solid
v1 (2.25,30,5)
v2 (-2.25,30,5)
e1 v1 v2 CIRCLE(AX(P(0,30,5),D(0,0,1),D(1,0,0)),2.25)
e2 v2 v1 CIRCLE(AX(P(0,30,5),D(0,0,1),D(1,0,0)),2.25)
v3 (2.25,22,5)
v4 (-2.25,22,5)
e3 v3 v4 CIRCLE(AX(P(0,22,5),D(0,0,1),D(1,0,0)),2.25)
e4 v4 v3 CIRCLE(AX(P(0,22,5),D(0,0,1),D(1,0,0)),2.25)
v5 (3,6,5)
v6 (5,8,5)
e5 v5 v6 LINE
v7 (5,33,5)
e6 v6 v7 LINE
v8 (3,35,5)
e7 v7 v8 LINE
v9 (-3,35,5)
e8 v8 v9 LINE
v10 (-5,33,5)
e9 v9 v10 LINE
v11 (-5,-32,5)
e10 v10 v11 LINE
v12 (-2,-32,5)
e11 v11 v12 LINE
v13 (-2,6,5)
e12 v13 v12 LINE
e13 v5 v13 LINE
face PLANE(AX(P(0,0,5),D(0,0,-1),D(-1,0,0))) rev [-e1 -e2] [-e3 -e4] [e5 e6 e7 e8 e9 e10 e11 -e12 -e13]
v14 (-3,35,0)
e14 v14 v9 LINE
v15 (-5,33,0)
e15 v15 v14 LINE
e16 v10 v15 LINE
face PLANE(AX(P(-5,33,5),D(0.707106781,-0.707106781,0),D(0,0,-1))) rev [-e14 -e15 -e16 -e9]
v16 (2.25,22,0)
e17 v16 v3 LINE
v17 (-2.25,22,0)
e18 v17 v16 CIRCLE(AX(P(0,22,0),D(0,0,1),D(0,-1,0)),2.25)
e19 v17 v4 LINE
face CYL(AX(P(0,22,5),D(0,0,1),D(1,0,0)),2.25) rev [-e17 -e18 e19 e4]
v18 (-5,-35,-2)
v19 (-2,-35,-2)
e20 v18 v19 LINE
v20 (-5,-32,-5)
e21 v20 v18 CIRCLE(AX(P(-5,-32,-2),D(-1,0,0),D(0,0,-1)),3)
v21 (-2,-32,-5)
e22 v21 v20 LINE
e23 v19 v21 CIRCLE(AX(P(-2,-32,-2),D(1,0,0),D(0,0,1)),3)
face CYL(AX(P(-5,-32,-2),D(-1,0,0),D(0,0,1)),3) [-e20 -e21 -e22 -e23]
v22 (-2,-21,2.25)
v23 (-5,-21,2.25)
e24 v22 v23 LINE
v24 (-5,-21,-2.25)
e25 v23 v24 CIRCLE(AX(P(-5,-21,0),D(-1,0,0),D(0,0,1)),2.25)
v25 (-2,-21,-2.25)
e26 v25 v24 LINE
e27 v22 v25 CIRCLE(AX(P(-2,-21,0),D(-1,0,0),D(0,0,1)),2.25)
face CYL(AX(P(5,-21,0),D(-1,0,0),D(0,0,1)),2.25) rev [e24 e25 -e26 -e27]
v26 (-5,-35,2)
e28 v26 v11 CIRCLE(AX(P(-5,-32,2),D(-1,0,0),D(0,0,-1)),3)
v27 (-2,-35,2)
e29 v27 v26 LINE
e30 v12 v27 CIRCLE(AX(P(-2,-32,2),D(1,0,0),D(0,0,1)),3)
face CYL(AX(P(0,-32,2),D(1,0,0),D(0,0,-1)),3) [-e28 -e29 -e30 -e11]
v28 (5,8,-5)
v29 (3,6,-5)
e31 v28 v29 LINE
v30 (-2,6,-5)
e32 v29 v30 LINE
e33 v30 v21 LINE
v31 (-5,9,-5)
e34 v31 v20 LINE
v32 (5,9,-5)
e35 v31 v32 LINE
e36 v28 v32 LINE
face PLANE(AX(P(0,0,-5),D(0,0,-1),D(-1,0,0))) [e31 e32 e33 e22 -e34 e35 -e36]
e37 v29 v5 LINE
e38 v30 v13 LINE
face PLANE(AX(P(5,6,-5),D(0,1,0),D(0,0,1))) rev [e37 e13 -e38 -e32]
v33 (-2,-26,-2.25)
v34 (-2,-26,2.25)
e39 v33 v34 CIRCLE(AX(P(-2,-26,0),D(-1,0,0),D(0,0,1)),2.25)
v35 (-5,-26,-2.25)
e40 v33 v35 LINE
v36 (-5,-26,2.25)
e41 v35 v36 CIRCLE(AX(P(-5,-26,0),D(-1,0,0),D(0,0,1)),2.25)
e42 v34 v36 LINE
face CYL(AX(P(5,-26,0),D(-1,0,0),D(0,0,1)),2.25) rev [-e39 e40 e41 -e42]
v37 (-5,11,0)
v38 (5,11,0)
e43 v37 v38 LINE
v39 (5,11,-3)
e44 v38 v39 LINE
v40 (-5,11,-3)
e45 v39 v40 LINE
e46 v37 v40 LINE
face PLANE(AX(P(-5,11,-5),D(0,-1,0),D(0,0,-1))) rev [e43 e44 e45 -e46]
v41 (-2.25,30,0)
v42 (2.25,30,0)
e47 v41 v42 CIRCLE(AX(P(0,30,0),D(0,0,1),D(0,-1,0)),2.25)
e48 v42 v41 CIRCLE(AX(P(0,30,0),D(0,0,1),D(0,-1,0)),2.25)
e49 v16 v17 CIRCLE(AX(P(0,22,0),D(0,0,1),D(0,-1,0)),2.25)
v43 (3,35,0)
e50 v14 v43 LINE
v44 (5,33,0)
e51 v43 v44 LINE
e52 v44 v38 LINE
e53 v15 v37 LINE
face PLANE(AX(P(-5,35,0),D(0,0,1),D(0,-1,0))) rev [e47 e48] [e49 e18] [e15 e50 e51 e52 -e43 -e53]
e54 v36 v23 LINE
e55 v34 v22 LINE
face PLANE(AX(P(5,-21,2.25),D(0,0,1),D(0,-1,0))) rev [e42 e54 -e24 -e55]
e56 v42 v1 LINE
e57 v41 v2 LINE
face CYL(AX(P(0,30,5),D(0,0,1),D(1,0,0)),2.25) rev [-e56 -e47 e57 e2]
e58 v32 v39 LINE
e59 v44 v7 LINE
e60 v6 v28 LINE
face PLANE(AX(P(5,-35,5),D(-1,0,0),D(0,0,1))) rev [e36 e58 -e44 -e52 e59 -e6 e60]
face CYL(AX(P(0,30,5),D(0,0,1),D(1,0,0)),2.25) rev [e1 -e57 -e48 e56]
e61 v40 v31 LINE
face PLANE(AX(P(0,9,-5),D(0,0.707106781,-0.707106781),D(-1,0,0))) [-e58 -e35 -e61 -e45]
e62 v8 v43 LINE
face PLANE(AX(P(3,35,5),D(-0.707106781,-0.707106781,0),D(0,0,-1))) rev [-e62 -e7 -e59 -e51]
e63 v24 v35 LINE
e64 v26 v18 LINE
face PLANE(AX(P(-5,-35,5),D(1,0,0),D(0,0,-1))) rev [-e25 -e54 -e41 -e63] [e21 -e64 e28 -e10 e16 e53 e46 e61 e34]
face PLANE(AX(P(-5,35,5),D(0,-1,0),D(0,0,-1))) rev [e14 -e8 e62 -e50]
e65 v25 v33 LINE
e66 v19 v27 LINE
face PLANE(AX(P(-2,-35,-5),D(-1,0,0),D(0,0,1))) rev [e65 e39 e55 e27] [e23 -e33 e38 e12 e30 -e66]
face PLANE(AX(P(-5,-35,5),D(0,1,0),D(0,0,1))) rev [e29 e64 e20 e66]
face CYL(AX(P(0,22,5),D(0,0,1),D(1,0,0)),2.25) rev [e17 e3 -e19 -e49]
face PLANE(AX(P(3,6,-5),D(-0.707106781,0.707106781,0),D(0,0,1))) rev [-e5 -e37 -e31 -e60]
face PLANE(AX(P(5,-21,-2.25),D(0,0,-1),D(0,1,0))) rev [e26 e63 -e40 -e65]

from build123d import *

# Parameters (mm, degrees)
SKETCH1_W            = 10
SKETCH1_H            = 70
BOSS_EXTRUDE1_DEPTH  = 5
SKETCH2_W            = 7
SKETCH2_H            = 41
CUT_EXTRUDE1_DEPTH   = 37.742346142
SKETCH3_W            = 5
SKETCH3_H            = 24
CUT_EXTRUDE2_DEPTH   = 37.742346142
CUT_EXTRUDE3_DEPTH   = 37.742346142
FILLET1_R            = 3
M4_CLEARANCE_HOLE1_D = 4.5
CHAMFER1_SIZE        = 2


with BuildPart() as part:
    # Sketch1 → Boss-Extrude1 (new, symmetric)
    with BuildSketch(Plane.XY):
        Rectangle(SKETCH1_W, SKETCH1_H)
    extrude(amount=BOSS_EXTRUDE1_DEPTH, both=True)

    # Sketch2 → Cut-Extrude1 (cut, through all)
    with BuildSketch(Plane.XY.offset(5)):
        with Locations((1.5, -14.5)):
            Rectangle(SKETCH2_W, SKETCH2_H)
    extrude(amount=-CUT_EXTRUDE1_DEPTH, mode=Mode.SUBTRACT)

    # Sketch3 → Cut-Extrude2 (cut, through all)
    with BuildSketch(Plane(origin=(5, 0, 0), x_dir=(0, 0, -1), z_dir=(1, 0, 0))):
        with Locations((2.5, 23)):
            Rectangle(SKETCH3_W, SKETCH3_H)
    extrude(amount=-CUT_EXTRUDE2_DEPTH, mode=Mode.SUBTRACT)

    # Sketch4 → Cut-Extrude3 (cut, through all)
    with BuildSketch(Plane.ZY.offset(5)):
        with BuildLine():
            Line((2.25, -21), (2.25, -26))
            ThreePointArc((2.25, -26), (0, -28.25), (-2.25, -26))
            Line((-2.25, -26), (-2.25, -21))
            ThreePointArc((-2.25, -21), (0, -18.75), (2.25, -21))
        make_face()
    extrude(amount=-CUT_EXTRUDE3_DEPTH, mode=Mode.SUBTRACT)

    # Fillet1
    fillet1_edges = [part.edges().sort_by_distance(p)[0] for p in [
        (-3.5, -35, 5),
        (-3.5, -35, -5),
    ]]
    fillet(fillet1_edges, radius=FILLET1_R)

    # M4 Clearance Hole1 (through all)
    with Locations(Plane.XY.offset(5)):
        with Locations((0, 30), (0, 22)):
            Hole(M4_CLEARANCE_HOLE1_D / 2)

    # Chamfer1
    chamfer1_edges = [part.edges().sort_by_distance(p)[0] for p in [
        (5, 6, 0),
        (0, 11, -5),
        (-5, 35, 2.5),
        (5, 35, 2.5),
    ]]
    chamfer(chamfer1_edges, length=CHAMFER1_SIZE)


solid = part.part
